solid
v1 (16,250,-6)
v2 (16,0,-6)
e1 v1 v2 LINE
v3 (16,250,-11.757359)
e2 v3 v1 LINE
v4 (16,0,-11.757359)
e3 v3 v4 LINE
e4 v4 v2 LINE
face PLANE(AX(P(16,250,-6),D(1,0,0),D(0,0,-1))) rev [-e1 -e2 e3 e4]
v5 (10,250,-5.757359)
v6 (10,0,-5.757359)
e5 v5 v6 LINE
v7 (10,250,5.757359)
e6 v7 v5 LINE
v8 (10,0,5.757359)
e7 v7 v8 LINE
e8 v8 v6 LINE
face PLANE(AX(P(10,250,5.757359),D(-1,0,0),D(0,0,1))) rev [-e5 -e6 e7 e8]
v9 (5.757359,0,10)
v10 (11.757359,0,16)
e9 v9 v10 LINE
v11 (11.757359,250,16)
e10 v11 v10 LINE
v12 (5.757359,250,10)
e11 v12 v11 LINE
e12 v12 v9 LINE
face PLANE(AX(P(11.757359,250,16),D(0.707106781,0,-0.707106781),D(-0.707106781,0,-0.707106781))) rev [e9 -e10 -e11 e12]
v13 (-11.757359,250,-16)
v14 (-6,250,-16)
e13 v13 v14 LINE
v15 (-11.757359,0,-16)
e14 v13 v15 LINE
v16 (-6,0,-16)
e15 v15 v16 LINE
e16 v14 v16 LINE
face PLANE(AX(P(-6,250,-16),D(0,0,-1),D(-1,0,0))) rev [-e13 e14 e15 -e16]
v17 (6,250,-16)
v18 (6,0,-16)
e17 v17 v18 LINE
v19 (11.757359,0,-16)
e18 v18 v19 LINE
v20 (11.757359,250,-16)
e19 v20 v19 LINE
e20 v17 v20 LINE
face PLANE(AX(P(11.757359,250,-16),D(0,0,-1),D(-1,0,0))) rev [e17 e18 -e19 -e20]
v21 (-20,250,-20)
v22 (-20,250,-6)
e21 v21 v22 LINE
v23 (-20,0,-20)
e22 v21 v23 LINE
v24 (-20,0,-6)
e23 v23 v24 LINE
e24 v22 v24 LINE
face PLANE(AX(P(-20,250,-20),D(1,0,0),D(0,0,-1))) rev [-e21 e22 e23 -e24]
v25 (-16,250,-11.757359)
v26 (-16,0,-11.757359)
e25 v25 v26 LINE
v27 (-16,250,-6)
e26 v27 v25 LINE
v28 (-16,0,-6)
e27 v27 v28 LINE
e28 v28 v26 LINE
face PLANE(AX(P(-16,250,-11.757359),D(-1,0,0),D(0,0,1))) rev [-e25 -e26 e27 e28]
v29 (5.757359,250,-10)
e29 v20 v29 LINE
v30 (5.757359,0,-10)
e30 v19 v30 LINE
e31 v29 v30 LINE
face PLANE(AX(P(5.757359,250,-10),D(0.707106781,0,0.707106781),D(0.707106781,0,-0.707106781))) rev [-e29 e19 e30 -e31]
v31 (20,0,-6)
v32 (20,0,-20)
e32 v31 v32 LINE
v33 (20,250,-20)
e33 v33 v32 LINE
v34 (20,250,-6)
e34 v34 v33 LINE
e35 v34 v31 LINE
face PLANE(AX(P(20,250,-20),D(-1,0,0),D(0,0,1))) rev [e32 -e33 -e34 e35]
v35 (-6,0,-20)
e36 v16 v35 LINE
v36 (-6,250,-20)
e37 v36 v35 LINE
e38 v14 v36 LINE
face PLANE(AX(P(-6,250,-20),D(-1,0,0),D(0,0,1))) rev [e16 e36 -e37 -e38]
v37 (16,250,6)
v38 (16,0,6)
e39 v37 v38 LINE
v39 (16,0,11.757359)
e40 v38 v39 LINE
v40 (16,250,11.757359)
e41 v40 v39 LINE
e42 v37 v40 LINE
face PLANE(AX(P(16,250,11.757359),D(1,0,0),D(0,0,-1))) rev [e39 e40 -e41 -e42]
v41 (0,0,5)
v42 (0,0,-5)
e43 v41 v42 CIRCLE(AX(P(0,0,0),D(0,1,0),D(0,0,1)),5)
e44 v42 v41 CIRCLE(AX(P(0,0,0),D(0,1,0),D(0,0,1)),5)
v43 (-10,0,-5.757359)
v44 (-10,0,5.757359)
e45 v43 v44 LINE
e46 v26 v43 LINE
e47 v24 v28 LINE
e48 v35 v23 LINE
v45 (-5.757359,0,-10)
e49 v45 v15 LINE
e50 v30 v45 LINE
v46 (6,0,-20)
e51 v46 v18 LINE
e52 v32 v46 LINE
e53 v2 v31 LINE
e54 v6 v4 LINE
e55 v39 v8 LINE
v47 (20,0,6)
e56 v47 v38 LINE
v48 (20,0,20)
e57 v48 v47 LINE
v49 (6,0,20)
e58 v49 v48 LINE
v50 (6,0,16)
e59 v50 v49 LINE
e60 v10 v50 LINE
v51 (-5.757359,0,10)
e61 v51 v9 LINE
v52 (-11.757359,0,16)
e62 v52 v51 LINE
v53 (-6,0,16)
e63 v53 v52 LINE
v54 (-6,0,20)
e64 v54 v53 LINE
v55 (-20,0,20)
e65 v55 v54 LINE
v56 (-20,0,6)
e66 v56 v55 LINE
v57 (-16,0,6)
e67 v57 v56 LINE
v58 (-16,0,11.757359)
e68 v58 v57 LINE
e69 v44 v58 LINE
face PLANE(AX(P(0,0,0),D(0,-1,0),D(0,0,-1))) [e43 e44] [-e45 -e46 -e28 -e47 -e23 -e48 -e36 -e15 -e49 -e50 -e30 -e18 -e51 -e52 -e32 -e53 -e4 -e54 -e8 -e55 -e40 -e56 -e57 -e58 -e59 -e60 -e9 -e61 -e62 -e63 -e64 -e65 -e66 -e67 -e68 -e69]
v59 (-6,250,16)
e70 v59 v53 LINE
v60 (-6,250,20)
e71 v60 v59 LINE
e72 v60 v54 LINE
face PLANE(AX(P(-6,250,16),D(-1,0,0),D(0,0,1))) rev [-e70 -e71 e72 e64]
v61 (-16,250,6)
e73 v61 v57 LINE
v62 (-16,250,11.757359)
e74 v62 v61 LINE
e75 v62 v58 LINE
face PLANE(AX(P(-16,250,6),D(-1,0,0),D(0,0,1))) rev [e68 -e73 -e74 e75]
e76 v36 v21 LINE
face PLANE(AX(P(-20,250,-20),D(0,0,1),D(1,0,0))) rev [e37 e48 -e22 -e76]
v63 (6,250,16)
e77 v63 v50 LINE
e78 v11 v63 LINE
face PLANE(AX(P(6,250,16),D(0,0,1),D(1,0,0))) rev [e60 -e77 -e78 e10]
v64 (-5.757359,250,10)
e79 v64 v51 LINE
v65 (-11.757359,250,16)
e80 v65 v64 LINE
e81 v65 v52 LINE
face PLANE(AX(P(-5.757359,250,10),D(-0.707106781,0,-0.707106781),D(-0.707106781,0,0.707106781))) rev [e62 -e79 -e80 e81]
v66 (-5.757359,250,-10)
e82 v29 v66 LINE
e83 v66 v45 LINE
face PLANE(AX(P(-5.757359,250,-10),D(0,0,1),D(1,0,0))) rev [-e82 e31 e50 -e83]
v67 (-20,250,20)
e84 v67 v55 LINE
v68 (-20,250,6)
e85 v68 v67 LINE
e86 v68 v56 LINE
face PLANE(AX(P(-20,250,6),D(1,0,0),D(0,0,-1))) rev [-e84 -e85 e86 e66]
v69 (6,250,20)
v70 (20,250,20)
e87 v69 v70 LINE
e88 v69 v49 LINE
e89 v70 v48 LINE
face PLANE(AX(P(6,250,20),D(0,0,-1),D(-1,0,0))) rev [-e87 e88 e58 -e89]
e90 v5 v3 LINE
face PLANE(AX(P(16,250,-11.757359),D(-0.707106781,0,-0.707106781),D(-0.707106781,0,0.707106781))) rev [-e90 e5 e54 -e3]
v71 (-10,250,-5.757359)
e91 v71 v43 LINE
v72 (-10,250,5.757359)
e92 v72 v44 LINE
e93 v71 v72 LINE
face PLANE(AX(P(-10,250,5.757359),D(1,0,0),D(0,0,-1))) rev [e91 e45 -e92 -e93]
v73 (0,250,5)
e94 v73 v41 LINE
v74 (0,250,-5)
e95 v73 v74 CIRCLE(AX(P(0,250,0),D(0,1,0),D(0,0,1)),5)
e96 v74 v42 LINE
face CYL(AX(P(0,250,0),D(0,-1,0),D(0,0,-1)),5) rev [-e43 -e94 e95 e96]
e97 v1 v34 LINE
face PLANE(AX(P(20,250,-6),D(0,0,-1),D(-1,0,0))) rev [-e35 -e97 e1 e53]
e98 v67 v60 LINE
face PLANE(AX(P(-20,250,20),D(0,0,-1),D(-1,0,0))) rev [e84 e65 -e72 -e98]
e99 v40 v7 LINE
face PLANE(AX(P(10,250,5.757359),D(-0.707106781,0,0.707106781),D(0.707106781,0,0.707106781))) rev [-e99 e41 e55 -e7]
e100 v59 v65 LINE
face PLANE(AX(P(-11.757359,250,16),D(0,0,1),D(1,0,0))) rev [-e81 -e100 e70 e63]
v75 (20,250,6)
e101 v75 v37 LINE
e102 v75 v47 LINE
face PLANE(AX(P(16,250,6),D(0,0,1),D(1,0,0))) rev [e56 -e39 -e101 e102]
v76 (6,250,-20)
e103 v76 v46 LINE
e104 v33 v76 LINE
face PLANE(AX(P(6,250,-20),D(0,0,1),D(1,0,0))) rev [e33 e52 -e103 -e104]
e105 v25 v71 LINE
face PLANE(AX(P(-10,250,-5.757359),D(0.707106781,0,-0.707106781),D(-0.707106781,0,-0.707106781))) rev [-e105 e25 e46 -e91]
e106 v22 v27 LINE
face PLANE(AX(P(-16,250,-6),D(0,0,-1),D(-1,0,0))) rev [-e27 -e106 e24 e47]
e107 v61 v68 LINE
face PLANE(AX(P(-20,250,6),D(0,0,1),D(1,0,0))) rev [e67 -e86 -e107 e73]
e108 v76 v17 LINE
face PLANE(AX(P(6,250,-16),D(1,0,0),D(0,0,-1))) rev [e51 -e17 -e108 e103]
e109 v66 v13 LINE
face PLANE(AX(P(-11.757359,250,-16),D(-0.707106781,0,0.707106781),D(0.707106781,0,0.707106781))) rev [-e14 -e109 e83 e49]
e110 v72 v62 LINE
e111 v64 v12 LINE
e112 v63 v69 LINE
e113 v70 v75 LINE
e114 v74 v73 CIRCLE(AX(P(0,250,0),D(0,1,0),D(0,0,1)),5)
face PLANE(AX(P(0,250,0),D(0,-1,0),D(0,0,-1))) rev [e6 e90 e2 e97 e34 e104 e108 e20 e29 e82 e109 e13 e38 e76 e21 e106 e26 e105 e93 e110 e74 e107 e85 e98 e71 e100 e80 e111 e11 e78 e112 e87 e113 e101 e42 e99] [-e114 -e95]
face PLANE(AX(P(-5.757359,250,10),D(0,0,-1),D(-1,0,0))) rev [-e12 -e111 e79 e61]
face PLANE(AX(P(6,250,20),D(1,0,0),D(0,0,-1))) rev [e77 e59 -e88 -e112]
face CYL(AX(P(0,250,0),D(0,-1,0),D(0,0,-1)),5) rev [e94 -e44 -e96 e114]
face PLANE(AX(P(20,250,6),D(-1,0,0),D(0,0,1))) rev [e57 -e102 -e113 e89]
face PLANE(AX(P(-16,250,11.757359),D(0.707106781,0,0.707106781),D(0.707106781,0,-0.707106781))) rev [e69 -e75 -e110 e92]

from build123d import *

# Parameters (mm, degrees)
SKETCH1_R           = 5
BOSS_EXTRUDE1_DEPTH = 250


with BuildPart() as part:
    # Sketch1 → Boss-Extrude1 (new body)
    with BuildSketch(Plane(origin=(0, 0, 0), x_dir=(1, 0, 0), z_dir=(0, 1, 0))):
        Polygon((-6, 20), (-6, 16), (-11.757359313, 16), (-5.757359313, 10), (5.757359313, 10), (11.757359313, 16), (6, 16), (6, 20), (20, 20), (20, 6), (16, 6), (16, 11.757359313), (10, 5.757359313), (10, -5.757359313), (16, -11.757359313), (16, -6), (20, -6), (20, -20), (6, -20), (6, -16), (11.757359313, -16), (5.757359313, -10), (-5.757359313, -10), (-11.757359313, -16), (-6, -16), (-6, -20), (-20, -20), (-20, -6), (-16, -6), (-16, -11.757359313), (-10, -5.757359313), (-10, 5.757359313), (-16, 11.757359313), (-16, 6), (-20, 6), (-20, 20), align=None)
        with Locations(Location((0, 0, 0), (0, 0, 270))):
            Circle(SKETCH1_R, mode=Mode.SUBTRACT)
    extrude(amount=BOSS_EXTRUDE1_DEPTH)


solid = part.part
